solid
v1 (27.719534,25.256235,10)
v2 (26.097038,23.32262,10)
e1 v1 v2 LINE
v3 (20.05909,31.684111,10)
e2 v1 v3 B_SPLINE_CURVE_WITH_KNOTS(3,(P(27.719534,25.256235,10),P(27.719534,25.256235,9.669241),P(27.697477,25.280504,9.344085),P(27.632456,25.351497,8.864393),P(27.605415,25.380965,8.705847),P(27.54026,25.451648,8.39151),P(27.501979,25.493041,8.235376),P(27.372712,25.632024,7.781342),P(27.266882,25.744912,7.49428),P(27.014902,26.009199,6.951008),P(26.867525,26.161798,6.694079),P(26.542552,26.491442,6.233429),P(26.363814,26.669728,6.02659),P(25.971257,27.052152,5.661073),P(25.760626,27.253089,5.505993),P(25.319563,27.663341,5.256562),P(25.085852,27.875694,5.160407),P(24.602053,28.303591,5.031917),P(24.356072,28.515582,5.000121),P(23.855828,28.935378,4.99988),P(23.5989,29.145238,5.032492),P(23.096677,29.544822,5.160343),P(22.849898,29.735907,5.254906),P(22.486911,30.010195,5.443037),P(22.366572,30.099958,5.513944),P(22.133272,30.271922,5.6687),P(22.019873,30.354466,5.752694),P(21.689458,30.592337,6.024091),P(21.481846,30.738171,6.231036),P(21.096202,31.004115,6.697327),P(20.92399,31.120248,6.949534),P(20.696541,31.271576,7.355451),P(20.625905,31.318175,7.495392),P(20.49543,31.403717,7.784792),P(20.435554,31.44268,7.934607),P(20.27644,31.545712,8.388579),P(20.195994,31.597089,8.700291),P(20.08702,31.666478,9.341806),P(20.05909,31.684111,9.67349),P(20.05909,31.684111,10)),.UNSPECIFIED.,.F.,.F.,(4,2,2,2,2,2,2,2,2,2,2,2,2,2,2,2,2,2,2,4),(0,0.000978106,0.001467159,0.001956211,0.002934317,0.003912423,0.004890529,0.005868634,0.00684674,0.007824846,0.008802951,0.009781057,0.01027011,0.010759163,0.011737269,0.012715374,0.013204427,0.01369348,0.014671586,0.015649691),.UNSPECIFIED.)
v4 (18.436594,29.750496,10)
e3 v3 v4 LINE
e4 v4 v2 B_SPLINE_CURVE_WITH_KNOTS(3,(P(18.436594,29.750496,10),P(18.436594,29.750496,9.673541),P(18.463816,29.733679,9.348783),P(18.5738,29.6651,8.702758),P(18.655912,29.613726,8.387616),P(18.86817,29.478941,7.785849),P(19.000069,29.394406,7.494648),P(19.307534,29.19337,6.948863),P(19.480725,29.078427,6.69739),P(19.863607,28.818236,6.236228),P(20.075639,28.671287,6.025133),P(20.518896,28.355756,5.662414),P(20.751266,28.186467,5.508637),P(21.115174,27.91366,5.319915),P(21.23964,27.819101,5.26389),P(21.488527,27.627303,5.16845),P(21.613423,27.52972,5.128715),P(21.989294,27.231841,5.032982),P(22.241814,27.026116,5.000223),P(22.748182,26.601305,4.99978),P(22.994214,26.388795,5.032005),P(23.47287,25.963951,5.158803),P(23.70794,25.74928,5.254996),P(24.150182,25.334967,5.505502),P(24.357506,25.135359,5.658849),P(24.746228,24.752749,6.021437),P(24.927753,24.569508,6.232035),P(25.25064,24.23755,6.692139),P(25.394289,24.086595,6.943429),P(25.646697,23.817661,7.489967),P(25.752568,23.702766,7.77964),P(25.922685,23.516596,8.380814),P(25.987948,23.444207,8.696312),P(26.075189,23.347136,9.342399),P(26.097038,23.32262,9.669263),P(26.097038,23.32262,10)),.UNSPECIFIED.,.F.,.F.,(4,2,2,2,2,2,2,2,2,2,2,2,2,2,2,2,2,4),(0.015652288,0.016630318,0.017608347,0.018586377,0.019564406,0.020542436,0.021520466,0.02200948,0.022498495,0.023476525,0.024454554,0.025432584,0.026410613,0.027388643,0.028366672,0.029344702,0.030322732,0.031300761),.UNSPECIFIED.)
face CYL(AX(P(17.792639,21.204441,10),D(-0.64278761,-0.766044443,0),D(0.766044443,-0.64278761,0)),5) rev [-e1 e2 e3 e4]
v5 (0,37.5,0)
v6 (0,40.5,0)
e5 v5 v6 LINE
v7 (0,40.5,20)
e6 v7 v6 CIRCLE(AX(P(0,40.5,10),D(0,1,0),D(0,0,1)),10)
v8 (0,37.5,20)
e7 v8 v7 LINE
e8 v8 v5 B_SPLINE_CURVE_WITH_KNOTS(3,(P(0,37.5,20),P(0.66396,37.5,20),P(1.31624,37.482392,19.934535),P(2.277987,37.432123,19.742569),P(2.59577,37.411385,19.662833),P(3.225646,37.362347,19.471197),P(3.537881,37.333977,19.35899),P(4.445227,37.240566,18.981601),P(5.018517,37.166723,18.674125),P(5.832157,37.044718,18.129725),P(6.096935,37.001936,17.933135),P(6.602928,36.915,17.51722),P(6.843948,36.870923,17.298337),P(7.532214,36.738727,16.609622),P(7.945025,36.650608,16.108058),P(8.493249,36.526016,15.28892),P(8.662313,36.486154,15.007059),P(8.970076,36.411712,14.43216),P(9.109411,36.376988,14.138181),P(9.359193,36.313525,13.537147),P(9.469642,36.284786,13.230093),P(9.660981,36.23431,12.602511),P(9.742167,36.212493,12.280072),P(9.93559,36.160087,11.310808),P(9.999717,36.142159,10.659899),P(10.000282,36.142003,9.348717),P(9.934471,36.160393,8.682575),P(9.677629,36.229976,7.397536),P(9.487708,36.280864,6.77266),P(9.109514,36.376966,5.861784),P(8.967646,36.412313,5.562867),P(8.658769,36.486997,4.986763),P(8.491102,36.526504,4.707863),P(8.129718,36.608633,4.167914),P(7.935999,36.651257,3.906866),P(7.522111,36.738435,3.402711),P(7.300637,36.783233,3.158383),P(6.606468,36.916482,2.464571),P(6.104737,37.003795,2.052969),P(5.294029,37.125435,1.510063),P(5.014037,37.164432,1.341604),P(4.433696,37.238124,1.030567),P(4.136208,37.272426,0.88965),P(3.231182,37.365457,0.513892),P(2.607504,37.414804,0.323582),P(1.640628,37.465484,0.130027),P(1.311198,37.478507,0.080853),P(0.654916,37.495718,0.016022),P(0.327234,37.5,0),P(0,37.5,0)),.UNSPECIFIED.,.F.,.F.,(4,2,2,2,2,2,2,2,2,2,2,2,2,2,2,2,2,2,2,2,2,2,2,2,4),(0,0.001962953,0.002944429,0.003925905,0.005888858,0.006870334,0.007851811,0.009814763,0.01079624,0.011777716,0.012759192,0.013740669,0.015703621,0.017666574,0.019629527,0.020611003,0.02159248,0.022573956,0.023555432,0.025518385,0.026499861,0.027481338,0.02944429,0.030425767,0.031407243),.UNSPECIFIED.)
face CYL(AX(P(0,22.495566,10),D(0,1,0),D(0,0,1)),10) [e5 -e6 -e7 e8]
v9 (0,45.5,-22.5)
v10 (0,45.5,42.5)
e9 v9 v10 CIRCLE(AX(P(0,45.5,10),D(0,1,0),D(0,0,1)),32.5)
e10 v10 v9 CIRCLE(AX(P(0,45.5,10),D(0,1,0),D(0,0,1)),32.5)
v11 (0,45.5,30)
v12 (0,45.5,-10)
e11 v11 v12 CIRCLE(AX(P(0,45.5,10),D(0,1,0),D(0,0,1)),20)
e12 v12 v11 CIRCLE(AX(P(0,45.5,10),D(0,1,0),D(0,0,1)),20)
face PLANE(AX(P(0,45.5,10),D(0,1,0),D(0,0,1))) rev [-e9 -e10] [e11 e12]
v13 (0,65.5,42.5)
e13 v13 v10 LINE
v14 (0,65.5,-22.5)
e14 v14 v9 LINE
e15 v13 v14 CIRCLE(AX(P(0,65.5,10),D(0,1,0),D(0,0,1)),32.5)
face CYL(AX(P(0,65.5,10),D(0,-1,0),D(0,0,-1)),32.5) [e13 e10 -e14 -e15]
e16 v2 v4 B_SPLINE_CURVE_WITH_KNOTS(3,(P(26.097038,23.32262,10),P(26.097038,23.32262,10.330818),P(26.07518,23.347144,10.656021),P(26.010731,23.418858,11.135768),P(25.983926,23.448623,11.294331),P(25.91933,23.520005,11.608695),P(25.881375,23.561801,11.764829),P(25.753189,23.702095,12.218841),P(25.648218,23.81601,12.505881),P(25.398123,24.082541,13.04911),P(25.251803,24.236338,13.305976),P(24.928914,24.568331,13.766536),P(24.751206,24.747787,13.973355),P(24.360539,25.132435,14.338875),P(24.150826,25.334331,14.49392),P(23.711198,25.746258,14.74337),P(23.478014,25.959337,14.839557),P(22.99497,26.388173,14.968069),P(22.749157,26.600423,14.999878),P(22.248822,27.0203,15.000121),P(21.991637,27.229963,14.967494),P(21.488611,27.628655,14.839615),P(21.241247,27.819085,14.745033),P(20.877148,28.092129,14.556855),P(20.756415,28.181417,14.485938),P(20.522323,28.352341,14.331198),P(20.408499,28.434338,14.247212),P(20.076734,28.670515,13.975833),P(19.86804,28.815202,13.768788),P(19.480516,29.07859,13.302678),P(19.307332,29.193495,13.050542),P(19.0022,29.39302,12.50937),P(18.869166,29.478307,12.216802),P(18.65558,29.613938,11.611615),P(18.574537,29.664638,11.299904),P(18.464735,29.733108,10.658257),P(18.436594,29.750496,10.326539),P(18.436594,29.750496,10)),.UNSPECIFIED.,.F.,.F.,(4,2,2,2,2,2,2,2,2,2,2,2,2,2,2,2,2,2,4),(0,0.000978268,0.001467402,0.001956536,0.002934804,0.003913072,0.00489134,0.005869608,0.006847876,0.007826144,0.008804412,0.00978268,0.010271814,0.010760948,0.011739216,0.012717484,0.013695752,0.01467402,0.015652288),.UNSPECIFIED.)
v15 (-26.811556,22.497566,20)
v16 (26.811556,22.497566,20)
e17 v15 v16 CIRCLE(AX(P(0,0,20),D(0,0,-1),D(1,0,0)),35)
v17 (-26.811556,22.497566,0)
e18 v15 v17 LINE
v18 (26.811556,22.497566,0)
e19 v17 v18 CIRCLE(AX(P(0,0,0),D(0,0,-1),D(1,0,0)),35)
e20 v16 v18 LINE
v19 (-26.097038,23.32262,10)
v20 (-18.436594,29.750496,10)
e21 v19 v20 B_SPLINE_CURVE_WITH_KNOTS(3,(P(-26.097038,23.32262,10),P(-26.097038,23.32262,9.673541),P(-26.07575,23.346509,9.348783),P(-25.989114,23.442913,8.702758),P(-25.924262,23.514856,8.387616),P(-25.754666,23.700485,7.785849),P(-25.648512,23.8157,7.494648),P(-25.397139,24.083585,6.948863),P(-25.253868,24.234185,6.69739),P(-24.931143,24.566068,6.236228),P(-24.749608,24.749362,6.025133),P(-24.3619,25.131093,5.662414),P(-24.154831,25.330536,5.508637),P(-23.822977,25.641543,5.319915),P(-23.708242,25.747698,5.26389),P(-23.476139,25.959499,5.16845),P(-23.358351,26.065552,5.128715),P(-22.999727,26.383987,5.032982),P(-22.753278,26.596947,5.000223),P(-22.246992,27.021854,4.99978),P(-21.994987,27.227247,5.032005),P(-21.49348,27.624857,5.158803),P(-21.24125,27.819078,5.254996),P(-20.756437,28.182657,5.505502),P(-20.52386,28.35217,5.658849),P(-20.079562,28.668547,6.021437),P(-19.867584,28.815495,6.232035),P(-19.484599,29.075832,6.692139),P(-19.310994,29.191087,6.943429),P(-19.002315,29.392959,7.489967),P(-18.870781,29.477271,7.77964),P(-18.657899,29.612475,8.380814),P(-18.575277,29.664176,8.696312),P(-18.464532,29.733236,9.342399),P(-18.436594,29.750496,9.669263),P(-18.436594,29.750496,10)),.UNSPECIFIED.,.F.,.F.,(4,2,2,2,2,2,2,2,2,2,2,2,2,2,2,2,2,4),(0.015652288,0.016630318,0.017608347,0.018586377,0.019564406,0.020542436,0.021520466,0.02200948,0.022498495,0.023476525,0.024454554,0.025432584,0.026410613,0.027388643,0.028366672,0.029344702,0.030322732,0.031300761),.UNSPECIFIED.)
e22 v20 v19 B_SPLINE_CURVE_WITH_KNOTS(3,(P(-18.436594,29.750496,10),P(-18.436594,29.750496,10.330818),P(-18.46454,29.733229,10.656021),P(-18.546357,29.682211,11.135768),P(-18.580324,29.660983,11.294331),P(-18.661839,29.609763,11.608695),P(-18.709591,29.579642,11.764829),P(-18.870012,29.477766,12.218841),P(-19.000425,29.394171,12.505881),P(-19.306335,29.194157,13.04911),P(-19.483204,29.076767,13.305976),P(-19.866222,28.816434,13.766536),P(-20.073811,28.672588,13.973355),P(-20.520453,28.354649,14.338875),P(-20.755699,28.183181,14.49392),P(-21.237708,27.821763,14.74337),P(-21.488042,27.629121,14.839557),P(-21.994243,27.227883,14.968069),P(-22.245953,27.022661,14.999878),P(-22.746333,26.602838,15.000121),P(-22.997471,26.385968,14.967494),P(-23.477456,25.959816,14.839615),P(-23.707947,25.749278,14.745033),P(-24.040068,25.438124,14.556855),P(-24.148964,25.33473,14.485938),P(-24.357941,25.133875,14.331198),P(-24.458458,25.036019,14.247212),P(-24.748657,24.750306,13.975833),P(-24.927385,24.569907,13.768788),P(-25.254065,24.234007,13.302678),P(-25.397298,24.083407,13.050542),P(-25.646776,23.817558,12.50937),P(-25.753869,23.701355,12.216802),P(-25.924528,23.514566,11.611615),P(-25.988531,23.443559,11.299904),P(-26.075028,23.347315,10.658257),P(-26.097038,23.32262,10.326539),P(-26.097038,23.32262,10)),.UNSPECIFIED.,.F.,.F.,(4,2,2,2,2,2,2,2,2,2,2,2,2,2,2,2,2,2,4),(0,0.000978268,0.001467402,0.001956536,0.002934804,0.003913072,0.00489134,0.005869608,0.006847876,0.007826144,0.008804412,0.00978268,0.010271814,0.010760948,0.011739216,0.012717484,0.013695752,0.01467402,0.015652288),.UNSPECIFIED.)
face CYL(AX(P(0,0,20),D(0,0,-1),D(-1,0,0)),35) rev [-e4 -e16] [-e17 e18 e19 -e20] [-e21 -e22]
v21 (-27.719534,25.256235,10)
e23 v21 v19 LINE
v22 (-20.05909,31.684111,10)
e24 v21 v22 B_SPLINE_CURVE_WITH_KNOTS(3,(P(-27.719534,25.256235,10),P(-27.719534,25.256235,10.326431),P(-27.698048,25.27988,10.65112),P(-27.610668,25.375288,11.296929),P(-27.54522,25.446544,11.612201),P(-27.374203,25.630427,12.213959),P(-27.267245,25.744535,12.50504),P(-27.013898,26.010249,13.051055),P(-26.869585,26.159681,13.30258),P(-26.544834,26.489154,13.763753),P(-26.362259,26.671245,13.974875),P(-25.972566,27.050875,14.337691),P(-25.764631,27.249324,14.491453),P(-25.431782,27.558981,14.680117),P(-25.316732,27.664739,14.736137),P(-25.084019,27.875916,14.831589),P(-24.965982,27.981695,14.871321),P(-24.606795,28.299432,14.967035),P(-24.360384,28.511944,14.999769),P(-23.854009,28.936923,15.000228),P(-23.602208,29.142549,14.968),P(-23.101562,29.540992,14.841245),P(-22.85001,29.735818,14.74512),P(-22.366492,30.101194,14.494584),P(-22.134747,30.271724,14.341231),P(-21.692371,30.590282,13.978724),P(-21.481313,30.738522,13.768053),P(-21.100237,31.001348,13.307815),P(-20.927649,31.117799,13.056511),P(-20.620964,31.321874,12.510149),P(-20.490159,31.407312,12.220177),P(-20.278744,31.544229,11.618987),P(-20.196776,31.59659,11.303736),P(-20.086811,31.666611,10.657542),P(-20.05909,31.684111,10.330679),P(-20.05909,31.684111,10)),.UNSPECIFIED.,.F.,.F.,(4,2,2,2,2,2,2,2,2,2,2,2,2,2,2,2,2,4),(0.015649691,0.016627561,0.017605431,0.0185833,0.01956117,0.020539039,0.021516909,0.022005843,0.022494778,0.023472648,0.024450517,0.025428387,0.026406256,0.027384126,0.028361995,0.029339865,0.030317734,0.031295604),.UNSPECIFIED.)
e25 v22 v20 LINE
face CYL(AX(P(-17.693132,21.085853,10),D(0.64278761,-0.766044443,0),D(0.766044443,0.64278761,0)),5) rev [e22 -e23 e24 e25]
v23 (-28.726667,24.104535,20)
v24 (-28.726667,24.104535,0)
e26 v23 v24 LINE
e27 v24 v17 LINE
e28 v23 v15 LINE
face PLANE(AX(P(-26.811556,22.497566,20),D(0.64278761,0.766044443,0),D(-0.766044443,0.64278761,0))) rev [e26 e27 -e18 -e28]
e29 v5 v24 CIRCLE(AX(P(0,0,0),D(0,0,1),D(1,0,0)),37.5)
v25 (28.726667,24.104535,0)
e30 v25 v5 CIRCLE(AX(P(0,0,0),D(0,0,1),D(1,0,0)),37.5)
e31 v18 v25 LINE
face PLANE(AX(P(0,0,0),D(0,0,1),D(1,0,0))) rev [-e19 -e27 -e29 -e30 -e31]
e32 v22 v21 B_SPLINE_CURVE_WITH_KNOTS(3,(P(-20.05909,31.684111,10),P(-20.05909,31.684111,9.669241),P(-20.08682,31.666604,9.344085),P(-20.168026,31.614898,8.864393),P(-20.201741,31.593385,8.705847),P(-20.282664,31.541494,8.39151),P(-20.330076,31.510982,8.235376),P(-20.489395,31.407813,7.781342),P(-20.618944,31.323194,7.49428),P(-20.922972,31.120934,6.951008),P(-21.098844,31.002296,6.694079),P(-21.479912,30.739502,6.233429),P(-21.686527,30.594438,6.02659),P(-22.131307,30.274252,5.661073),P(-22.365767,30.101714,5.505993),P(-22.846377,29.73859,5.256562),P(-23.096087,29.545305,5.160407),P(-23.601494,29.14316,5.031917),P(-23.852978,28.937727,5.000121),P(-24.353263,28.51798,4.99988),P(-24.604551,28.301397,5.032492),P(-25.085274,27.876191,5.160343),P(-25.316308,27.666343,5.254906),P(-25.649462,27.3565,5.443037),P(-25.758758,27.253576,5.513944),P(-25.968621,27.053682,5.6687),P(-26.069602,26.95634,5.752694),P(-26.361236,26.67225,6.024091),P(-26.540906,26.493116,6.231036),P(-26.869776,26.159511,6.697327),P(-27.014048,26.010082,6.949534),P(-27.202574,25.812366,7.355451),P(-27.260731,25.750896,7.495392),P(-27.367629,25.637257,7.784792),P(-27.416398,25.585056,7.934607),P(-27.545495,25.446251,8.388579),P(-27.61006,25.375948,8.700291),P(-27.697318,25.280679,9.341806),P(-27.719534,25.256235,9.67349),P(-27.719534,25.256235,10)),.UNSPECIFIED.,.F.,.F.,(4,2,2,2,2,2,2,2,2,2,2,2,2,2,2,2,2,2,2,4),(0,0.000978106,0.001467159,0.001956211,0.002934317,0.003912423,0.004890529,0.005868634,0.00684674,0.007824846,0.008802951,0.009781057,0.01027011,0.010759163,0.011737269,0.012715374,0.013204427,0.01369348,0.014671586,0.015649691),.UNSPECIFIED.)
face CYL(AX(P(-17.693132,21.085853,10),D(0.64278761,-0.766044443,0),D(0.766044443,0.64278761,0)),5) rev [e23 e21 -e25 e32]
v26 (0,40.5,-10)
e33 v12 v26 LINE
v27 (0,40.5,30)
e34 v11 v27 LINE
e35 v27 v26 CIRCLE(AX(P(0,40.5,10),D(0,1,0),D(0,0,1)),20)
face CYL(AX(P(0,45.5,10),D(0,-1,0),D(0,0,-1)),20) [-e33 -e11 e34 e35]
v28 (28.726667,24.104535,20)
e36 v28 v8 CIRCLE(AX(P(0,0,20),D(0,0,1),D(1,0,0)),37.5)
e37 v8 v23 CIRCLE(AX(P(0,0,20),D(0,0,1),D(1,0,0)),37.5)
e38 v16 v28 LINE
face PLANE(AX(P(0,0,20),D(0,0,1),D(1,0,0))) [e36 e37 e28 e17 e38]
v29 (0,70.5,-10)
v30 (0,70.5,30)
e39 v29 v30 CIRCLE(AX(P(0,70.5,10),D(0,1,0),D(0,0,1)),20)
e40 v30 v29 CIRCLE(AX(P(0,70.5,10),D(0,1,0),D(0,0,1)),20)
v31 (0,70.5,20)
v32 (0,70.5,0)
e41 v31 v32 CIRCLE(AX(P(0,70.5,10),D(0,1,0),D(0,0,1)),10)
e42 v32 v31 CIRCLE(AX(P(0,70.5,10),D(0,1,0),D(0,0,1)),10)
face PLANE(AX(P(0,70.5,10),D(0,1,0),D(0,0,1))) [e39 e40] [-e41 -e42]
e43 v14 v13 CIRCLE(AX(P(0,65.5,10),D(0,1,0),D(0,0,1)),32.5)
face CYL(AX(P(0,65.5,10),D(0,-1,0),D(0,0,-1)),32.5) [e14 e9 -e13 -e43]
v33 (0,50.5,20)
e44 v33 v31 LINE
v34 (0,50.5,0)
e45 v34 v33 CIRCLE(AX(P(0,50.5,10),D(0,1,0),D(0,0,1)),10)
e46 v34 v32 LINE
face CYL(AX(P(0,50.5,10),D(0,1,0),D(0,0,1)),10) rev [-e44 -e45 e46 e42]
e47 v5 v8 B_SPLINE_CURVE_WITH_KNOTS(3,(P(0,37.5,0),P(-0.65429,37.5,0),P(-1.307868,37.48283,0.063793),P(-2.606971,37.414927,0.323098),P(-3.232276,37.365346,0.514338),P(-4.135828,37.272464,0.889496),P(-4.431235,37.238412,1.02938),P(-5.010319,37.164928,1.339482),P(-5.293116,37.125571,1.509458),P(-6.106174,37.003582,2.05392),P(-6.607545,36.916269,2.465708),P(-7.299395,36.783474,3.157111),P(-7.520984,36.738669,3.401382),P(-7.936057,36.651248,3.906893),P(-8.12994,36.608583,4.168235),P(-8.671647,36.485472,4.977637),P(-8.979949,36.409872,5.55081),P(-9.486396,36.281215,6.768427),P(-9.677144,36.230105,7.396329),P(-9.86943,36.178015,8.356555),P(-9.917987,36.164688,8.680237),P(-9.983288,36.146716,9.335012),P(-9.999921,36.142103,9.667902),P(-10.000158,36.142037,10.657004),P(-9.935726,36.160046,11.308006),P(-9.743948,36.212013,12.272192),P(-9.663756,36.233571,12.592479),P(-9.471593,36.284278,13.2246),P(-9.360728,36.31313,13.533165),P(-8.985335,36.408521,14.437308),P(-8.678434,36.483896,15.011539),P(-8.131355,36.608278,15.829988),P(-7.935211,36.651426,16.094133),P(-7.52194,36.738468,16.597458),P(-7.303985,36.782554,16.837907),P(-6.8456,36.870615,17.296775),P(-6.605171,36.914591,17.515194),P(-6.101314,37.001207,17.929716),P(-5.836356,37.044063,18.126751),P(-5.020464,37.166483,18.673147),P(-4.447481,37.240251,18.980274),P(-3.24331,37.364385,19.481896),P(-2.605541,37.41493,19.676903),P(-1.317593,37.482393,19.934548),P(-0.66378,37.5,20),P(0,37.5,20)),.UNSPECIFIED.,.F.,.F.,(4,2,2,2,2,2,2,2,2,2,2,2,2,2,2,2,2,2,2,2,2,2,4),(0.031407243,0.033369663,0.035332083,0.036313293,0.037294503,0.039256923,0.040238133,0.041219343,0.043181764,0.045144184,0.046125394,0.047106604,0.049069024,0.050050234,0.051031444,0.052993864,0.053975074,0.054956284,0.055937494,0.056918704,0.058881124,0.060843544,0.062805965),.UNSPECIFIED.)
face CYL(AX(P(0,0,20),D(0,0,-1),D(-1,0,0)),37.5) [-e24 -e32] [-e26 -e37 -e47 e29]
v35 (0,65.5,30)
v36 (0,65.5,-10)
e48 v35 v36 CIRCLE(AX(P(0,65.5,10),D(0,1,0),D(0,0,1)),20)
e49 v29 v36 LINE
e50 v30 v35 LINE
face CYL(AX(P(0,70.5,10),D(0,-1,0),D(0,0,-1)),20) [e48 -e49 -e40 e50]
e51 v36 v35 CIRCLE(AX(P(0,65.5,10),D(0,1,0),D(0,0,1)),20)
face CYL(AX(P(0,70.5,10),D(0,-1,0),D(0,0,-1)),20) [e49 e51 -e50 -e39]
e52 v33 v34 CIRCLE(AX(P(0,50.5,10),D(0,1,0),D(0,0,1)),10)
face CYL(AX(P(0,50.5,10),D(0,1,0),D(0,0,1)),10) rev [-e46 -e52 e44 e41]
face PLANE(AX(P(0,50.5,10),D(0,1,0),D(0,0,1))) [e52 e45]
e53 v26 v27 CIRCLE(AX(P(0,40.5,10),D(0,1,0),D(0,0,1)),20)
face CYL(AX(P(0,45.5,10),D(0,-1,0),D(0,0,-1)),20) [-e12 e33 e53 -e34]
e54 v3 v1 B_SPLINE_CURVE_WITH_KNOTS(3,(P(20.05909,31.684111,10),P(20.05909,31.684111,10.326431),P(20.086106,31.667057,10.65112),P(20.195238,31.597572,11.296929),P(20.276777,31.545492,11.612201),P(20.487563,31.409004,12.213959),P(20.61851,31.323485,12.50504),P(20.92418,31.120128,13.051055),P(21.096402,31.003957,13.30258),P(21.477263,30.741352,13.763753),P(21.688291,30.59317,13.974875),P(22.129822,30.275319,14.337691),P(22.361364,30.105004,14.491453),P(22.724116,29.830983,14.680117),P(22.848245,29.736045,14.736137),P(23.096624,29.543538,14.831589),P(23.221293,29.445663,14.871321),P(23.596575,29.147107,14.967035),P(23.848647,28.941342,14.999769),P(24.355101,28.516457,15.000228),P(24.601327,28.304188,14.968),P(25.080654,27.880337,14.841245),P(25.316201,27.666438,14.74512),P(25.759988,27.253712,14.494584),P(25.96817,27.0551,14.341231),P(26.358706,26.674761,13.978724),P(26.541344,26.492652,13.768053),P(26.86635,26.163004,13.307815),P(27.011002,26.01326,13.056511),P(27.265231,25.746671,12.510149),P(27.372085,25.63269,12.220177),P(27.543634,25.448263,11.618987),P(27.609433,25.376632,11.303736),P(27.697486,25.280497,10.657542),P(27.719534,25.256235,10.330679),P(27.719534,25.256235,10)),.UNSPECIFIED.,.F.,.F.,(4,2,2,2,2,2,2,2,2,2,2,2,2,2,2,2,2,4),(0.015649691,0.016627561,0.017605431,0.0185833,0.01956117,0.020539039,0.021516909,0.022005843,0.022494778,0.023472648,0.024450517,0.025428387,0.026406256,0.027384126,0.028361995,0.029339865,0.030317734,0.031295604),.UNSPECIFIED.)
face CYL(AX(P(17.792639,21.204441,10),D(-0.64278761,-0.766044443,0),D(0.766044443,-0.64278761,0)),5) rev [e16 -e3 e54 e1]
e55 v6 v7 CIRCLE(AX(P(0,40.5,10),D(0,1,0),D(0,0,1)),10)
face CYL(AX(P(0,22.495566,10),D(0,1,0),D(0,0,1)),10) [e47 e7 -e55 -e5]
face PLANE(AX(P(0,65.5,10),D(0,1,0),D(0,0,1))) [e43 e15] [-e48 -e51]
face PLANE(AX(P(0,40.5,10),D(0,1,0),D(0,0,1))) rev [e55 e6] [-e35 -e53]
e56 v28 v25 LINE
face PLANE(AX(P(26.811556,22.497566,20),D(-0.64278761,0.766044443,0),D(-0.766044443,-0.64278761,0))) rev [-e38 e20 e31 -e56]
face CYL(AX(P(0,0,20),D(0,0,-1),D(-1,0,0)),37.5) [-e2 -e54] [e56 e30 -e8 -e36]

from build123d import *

# Parameters (mm, degrees)
BOSS_EXTRUDE4_DEPTH      = 20
BOSS_EXTRUDE5_REACH      = 41.361
BOSS_EXTRUDE5_END_RADIUS = 37.5
SKETCH8_R                = 10
SKETCH9_R                = 20
BOSS_EXTRUDE6_DEPTH      = 5
SKETCH10_R               = 32.5
BOSS_EXTRUDE7_DEPTH      = 20
SKETCH11_R               = 20
BOSS_EXTRUDE8_DEPTH      = 5
SKETCH12_R               = 10
CUT_EXTRUDE3_DEPTH       = 20


with BuildPart() as part:
    # Sketch4 → Boss-Extrude4 (new body)
    with BuildSketch(Plane.XY):
        with BuildLine():
            Line((-26.811555509, 22.497566339), (-28.726666617, 24.104535363))
            ThreePointArc((-28.726666617, 24.104535363), (0, 37.5), (28.726666617, 24.104535363))
            Line((28.726666617, 24.104535363), (26.811555509, 22.497566339))
            ThreePointArc((26.811555509, 22.497566339), (0, 35), (-26.811555509, 22.497566339))
        make_face()
    extrude(amount=BOSS_EXTRUDE4_DEPTH)

    # Boss-Extrude5: up to this cylinder (the profile starts outside it)
    boss_extrude5_end = Plane(origin=(0, 0, 10), z_dir=(0, 0, -1)) * Cylinder(BOSS_EXTRUDE5_END_RADIUS, 158.722, mode=Mode.PRIVATE)
    # Sketch8 → Boss-Extrude5 (add, up to the surface)
    with BuildSketch(Plane(origin=(0, 40.5, 0), x_dir=(1, 0, 0), z_dir=(0, 1, 0)), mode=Mode.PRIVATE) as boss_extrude5_sk1:
        with Locations(Location((0, -10, 0), (0, 0, 270))):
            Circle(SKETCH8_R)
    boss_extrude5_tool1 = extrude(boss_extrude5_sk1.sketch, amount=-BOSS_EXTRUDE5_REACH, mode=Mode.PRIVATE) - boss_extrude5_end
    add(boss_extrude5_tool1.solids().sort_by_distance((0, 40.5, 10))[0])

    # Sketch9 → Boss-Extrude6 (add)
    with BuildSketch(Plane(origin=(0, 40.5, 0), x_dir=(1, 0, 0), z_dir=(0, 1, 0))):
        with Locations(Location((0, -10, 0), (0, 0, 270))):
            Circle(SKETCH9_R)
    extrude(amount=BOSS_EXTRUDE6_DEPTH)

    # Sketch10 → Boss-Extrude7 (add)
    with BuildSketch(Plane(origin=(0, 45.5, 0), x_dir=(1, 0, 0), z_dir=(0, 1, 0))):
        with Locations(Location((0, -10, 0), (0, 0, 270))):
            Circle(SKETCH10_R)
    extrude(amount=BOSS_EXTRUDE7_DEPTH)

    # Sketch11 → Boss-Extrude8 (add)
    with BuildSketch(Plane(origin=(0, 65.5, 0), x_dir=(1, 0, 0), z_dir=(0, 1, 0))):
        with Locations(Location((0, -10, 0), (0, 0, 270))):
            Circle(SKETCH11_R)
    extrude(amount=BOSS_EXTRUDE8_DEPTH)

    # Sketch12 → Cut-Extrude3 (cut)
    with BuildSketch(Plane(origin=(0, 70.5, 0), x_dir=(1, 0, 0), z_dir=(0, 1, 0))):
        with Locations(Location((0, -10, 0), (0, 0, 270))):
            Circle(SKETCH12_R)
    extrude(amount=-CUT_EXTRUDE3_DEPTH, mode=Mode.SUBTRACT)

    # Sketch15 → Cut-Revolve3 (revolve, cut)
    with BuildSketch(Plane.XY.offset(10), mode=Mode.PRIVATE) as cut_revolve3_sk:
        Polygon((-17.693131792, 21.085853377), (-26.278152948, 31.317083182), (-30.108375164, 28.103145134), (-21.523354007, 17.871915328), align=None)
    revolve(cut_revolve3_sk.sketch.rotate(Axis((-17.693131792, 21.085853377, 10), (-0.6427876096865413, 0.7660444431189765, 0)), 180), axis=Axis((-17.693131792, 21.085853377, 10), (-0.6427876096865413, 0.7660444431189765, 0)), mode=Mode.SUBTRACT)

    # Sketch16 → Cut-Revolve4 (revolve, cut)
    with BuildSketch(Plane.XY.offset(10), mode=Mode.PRIVATE) as cut_revolve4_sk:
        Polygon((17.792638641, 21.204441023), (27.637153268, 32.936676696), (23.806931052, 36.150614744), (13.962416426, 24.418379071), align=None)
    revolve(cut_revolve4_sk.sketch.rotate(Axis((17.792638641, 21.204441023, 10), (0.6427876096865399, 0.7660444431189776, 0)), 180), axis=Axis((17.792638641, 21.204441023, 10), (0.6427876096865399, 0.7660444431189776, 0)), mode=Mode.SUBTRACT)


solid = part.part
